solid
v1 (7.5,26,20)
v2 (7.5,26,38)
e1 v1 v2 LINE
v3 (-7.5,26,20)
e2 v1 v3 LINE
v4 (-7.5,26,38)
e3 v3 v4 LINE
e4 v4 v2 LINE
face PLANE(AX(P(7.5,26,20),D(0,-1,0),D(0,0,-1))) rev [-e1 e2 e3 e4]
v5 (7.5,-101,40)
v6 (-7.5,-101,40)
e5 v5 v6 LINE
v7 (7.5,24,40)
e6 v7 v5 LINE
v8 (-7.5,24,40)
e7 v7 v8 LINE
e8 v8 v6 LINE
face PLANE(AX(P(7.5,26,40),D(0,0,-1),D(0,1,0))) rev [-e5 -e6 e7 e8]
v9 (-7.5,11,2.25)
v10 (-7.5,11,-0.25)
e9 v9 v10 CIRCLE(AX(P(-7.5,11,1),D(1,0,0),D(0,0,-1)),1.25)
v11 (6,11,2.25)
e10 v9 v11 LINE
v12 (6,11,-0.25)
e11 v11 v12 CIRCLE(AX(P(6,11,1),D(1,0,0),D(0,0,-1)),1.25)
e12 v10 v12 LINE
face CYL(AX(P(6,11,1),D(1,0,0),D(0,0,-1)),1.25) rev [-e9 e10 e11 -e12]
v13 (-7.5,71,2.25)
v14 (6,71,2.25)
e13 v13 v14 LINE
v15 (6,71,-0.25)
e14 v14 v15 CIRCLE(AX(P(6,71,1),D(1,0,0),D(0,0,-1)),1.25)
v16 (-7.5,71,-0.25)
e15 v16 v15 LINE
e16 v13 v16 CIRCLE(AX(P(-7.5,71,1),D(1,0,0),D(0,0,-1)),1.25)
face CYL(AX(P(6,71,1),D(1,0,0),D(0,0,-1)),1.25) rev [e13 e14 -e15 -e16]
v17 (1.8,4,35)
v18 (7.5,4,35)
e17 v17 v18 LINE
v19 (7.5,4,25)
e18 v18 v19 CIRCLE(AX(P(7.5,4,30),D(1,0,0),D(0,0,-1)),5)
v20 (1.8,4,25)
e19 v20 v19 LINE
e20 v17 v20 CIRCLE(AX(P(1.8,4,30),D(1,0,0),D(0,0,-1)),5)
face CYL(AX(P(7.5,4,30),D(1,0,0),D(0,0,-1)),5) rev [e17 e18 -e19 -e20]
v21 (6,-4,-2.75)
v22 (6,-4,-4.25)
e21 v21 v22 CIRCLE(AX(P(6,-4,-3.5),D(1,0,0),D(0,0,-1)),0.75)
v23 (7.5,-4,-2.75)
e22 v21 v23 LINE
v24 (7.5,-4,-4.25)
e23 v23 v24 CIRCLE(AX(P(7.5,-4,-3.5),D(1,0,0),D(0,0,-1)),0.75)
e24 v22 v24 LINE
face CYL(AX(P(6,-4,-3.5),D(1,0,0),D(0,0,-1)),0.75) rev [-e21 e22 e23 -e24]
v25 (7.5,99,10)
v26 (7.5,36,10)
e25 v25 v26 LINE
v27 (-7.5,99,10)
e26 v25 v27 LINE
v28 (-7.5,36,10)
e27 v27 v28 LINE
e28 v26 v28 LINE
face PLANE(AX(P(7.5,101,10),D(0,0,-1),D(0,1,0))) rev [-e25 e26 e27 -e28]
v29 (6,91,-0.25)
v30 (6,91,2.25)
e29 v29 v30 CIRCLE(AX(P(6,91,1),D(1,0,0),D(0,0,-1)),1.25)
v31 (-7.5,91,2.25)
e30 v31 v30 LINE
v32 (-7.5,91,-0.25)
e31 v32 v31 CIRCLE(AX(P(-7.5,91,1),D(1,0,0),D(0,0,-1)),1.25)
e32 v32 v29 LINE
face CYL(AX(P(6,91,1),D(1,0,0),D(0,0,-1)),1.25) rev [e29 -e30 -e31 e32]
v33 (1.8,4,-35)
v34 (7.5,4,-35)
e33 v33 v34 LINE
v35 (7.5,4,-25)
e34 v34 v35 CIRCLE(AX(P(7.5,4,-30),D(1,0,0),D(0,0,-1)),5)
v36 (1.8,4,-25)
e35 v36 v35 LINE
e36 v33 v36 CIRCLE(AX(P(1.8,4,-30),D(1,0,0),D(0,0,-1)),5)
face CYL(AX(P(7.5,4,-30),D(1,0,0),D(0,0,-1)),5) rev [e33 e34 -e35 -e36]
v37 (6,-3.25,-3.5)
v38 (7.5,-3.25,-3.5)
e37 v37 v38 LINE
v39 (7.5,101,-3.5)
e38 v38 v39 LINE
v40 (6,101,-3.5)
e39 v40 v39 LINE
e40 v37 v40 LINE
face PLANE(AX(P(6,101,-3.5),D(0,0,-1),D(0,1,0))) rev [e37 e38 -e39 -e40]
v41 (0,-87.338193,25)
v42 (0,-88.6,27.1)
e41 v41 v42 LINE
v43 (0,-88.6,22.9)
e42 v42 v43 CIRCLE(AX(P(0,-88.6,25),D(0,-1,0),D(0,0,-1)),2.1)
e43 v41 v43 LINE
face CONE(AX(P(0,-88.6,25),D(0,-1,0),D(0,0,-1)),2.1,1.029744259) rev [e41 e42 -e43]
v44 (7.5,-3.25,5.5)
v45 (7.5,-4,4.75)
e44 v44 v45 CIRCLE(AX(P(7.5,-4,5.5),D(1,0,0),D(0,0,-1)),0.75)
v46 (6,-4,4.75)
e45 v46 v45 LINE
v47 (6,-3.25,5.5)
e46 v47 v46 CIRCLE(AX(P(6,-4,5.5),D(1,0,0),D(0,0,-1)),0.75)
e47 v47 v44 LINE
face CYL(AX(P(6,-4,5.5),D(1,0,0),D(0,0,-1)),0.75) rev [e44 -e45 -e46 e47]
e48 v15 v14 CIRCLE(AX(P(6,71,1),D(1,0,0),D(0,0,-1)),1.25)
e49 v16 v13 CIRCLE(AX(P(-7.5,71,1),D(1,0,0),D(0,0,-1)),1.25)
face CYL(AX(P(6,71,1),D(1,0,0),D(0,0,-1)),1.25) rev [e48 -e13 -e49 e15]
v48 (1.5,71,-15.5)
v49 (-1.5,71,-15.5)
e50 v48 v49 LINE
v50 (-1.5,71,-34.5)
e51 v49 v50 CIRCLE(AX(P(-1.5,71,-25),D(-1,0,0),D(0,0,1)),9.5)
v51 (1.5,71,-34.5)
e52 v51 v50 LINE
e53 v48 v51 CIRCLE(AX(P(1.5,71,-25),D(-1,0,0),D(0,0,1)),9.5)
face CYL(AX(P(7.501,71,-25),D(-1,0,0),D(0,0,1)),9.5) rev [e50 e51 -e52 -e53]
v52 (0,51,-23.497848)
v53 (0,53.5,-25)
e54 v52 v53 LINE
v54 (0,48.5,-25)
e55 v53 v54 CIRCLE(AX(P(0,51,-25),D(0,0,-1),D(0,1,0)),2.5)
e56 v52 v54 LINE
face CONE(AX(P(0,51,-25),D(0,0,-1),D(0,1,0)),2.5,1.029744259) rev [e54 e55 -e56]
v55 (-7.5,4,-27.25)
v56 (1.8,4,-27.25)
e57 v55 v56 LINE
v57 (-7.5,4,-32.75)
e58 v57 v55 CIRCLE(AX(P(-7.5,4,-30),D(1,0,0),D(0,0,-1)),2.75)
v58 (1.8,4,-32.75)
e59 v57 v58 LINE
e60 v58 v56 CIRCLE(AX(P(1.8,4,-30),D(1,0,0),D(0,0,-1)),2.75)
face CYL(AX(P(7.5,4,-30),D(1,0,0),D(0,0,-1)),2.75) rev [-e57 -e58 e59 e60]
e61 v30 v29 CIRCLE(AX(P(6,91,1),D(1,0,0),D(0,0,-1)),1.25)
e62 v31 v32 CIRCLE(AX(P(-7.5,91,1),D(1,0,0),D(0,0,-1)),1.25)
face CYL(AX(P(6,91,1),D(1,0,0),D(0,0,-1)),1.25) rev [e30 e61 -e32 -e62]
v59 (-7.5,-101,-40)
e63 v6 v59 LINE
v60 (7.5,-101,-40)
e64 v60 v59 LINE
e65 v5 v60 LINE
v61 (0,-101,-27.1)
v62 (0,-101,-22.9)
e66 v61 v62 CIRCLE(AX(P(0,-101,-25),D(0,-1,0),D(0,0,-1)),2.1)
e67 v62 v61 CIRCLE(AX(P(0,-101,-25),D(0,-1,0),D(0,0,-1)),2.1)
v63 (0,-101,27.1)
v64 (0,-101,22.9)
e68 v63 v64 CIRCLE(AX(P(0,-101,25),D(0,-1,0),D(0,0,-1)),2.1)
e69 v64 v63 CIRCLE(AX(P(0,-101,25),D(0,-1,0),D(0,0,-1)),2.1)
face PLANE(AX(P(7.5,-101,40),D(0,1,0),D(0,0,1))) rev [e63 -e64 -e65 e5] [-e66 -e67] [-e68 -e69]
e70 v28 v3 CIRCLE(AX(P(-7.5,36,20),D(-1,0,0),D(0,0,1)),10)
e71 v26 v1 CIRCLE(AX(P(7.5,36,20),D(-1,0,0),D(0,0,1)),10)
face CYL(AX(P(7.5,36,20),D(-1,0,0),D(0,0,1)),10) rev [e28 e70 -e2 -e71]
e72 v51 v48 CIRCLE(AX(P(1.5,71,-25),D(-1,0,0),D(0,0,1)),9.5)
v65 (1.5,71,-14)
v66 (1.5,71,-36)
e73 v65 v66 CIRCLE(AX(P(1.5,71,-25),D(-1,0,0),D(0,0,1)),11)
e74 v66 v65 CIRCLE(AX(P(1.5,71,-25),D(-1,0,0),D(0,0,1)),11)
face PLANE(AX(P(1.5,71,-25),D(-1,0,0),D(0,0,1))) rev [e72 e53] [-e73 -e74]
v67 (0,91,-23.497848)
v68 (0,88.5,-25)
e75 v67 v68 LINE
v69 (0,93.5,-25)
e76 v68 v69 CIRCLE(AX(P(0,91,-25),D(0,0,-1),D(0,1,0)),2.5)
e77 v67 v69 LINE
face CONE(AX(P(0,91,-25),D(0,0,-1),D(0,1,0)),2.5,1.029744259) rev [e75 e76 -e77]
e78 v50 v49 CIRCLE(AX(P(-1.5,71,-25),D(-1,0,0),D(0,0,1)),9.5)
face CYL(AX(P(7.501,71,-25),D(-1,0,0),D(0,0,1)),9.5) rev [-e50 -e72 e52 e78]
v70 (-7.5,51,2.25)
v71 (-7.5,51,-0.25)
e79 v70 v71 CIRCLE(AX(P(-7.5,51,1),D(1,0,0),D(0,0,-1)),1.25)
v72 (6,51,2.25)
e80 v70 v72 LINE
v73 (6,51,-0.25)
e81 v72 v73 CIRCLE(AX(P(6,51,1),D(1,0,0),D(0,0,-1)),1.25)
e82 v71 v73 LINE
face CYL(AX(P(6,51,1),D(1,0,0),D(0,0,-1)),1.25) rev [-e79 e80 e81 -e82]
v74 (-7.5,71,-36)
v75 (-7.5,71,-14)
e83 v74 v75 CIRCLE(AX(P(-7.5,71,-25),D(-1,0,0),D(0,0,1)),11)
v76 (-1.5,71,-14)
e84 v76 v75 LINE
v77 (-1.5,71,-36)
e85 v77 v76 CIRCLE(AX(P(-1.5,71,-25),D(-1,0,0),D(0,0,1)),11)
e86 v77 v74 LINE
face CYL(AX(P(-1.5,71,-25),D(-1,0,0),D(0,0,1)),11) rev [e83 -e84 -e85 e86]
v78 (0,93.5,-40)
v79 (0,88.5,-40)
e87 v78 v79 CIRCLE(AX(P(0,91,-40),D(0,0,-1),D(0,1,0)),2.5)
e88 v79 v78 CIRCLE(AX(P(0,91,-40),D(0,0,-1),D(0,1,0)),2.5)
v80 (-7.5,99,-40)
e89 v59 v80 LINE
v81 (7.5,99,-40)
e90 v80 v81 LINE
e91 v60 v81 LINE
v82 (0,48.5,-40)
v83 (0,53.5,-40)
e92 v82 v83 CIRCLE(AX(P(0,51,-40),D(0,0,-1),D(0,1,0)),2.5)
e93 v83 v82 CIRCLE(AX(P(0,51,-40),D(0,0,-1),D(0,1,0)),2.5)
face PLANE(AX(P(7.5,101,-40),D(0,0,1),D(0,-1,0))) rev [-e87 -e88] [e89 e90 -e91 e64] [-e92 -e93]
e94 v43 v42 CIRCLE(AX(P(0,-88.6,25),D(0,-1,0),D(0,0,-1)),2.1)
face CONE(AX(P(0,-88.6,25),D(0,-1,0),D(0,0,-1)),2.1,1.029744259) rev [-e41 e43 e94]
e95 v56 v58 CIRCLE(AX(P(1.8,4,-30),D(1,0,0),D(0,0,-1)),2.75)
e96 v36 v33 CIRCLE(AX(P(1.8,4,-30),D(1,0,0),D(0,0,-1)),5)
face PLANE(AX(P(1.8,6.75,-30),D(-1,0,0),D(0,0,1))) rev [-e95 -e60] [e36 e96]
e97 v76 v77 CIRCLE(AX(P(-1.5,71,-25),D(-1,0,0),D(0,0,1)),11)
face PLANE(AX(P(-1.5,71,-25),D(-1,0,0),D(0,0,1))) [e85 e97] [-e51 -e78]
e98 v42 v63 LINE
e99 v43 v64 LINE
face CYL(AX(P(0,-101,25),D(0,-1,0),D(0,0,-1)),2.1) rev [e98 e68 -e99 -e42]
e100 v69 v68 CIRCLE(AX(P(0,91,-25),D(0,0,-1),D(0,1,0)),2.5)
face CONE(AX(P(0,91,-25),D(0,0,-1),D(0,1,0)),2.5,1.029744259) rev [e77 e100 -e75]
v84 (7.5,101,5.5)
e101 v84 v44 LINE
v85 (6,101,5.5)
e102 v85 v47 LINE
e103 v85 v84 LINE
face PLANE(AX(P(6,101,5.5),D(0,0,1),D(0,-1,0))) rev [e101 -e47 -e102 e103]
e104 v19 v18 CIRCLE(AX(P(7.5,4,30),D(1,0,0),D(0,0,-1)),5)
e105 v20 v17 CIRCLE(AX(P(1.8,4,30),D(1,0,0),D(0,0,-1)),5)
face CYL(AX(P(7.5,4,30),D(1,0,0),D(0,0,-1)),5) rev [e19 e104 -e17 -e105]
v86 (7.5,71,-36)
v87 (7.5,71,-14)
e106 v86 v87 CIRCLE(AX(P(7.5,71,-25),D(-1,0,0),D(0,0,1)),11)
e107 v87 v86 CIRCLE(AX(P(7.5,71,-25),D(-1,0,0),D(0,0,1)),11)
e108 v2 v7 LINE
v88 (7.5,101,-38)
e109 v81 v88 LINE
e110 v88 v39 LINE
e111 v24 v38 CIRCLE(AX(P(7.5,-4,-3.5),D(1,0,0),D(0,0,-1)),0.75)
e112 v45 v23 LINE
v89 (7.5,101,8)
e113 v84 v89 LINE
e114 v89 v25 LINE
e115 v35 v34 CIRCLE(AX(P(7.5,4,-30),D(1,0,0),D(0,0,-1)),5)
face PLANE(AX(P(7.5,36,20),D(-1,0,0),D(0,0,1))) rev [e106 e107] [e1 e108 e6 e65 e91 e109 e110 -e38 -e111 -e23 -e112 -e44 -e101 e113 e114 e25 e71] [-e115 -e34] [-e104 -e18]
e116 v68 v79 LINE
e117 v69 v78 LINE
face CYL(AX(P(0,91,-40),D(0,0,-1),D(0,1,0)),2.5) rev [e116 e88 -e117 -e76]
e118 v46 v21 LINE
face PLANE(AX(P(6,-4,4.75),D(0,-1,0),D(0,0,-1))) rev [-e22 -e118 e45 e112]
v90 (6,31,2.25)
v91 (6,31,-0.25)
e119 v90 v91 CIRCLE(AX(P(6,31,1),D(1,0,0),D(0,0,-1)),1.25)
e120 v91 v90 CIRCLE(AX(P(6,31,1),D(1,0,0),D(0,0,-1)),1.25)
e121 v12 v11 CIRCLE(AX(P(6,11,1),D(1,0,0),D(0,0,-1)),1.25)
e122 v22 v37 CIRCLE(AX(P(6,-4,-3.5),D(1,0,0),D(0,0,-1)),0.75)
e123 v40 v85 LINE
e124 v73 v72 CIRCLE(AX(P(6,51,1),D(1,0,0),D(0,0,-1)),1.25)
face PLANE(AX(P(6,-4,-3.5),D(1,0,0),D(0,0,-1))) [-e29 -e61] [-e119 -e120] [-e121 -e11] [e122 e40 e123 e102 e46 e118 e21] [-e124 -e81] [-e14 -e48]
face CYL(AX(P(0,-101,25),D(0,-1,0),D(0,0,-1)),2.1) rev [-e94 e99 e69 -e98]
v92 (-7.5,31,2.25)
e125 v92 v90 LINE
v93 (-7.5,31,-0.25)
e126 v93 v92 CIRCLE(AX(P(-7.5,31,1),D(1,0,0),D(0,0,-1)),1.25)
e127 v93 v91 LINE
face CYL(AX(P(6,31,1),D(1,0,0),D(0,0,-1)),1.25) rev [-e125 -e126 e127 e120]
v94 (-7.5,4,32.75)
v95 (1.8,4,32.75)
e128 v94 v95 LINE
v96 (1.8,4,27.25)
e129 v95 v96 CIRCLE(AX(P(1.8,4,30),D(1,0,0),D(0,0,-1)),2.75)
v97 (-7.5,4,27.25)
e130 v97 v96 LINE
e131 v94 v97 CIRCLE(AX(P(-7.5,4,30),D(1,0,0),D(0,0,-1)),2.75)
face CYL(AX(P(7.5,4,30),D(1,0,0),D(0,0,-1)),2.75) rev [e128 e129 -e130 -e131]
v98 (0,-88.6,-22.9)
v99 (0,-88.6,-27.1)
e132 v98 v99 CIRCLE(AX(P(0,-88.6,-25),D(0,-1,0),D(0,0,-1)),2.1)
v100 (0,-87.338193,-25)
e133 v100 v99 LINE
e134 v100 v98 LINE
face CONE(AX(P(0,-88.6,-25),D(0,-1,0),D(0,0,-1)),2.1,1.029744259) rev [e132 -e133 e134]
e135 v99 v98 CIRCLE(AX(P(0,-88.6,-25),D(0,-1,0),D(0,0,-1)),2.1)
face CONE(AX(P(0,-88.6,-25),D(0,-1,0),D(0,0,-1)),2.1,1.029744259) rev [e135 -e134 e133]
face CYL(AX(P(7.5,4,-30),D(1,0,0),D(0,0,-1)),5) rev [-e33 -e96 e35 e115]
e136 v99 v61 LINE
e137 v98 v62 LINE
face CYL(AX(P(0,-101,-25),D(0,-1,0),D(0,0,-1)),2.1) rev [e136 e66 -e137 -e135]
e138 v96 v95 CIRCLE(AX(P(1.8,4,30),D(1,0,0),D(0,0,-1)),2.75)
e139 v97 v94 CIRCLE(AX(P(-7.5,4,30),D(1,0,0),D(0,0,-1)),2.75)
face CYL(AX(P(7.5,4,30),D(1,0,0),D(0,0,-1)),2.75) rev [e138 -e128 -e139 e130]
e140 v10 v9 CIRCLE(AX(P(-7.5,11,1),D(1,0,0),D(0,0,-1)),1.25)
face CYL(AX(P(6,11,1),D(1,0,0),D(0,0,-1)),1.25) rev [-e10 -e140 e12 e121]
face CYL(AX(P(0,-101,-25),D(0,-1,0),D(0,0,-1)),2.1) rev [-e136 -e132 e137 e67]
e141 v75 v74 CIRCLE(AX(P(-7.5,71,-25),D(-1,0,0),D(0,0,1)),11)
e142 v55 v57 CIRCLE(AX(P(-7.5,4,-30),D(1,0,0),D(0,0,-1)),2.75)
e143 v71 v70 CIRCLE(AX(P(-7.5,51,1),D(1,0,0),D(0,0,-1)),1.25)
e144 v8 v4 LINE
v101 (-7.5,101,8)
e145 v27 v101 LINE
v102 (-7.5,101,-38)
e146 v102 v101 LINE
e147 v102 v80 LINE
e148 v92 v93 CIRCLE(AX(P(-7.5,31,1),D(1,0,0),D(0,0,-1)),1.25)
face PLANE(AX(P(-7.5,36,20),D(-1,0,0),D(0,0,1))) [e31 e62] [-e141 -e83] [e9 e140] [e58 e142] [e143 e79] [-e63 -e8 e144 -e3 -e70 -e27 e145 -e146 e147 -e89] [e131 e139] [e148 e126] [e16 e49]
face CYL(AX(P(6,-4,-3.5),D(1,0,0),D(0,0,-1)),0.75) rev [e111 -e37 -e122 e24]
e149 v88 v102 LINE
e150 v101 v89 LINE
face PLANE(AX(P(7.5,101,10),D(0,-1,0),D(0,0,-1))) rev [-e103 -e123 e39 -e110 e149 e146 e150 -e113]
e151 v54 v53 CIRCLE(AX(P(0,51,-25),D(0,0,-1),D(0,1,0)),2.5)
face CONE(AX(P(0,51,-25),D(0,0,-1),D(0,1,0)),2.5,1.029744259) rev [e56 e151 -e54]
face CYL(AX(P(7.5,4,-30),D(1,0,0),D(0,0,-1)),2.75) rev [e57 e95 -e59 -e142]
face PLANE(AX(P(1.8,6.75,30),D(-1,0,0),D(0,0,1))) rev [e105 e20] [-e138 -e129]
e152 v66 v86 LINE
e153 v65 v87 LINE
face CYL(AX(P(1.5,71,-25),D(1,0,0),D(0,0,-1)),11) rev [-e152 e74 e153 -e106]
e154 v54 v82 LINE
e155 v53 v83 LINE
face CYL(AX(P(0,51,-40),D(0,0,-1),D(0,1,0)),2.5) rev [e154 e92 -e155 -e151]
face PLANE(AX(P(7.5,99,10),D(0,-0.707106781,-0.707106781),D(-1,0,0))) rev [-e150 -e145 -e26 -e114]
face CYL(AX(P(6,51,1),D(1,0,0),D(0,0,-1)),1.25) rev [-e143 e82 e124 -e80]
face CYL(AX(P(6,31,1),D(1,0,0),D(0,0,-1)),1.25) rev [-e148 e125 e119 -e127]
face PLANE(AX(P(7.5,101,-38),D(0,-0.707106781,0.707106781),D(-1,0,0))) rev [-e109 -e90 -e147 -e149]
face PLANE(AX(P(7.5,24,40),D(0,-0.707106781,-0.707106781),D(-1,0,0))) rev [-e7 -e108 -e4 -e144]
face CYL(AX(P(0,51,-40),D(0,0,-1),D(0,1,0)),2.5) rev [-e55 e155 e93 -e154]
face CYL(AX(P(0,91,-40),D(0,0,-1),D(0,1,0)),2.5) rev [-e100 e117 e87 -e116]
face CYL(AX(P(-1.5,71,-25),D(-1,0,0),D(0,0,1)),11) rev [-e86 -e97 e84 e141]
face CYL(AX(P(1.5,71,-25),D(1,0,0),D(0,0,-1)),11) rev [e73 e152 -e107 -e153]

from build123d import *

# Parameters (mm, degrees)
EXTRUDE_1_DEPTH           = 7.5
SKETCH_2_R                = 11
CUT_EXTRUDE_1_DEPTH       = 6
CUT_EXTRUDE_2_REACH       = 111.663
SKETCH_3_R                = 9.5
CUT_EXTRUDE_3_DEPTH       = 1.5
HOLE_WIZARD_M5_1_D        = 4.2
HOLE_WIZARD_M5_1_DEPTH    = 12.4
HOLE_WIZARD_M5_1_TIP      = 1.2618073
HOLE_WIZARD_1_D           = 5.5
HOLE_WIZARD_1_CBORE_D     = 10
HOLE_WIZARD_1_CBORE_DEPTH = 5.7
HOLE_WIZARD_M3_2_D        = 2.5
CUT_EXTRUDE_START         = -6
SKETCH_17_R               = 11
CUT_EXTRUDE_4_DEPTH       = 6
HOLE_WIZARD_M6_1_D        = 5
HOLE_WIZARD_M6_1_DEPTH    = 15
HOLE_WIZARD_M6_1_TIP      = 1.502151548
CHAMFER_1_SIZE            = 2


with BuildPart() as part:
    # 草图1 → 凸台-拉伸1 (new, symmetric)
    with BuildSketch(Plane(origin=(0, 0, 0), x_dir=(0, 0, -1), z_dir=(1, 0, 0))):
        with BuildLine():
            Line((-10, 101), (-10, 36))
            ThreePointArc((-10, 36), (-12.928932188, 28.928932188), (-20, 26))
            Line((-20, 26), (-40, 26))
            Line((-40, 26), (-40, -101))
            Line((-40, -101), (40, -101))
            Line((40, -101), (40, 101))
            Line((40, 101), (-10, 101))
        make_face()
    extrude(amount=EXTRUDE_1_DEPTH, both=True)

    # 草图2 → 切除-拉伸1 (cut)
    with BuildSketch(Plane.ZY.offset(-7.5)):
        with Locations((-25, 71)):
            Circle(SKETCH_2_R)
    extrude(amount=CUT_EXTRUDE_1_DEPTH, mode=Mode.SUBTRACT)

    # 草图3 → 切除-拉伸2 (cut, up to next)
    with BuildSketch(Plane(origin=(-7.5, 0, 0), x_dir=(0, 0, -1), z_dir=(1, 0, 0)), mode=Mode.PRIVATE) as cut_extrude_2_sk1:
        with Locations(Location((25, 71, 0), (0, 0, 180))):
            Circle(SKETCH_3_R)
    cut_extrude_2_tool1 = extrude(cut_extrude_2_sk1.sketch, amount=CUT_EXTRUDE_2_REACH, mode=Mode.PRIVATE) & part.part
    add(cut_extrude_2_tool1.solids().sort_by_distance((-7.5, 71, -25))[0], mode=Mode.SUBTRACT)

    # 草图6 → 切除-拉伸3 (cut)
    with BuildSketch(Plane(origin=(7.5, 0, 0), x_dir=(0, 0, -1), z_dir=(1, 0, 0))):
        with BuildLine():
            Line((-5.5, 101), (3.5, 101))
            Line((3.5, 101), (3.5, -3.25))
            ThreePointArc((3.5, -3.25), (4.030330086, -4.530330086), (2.75, -4))
            Line((2.75, -4), (-4.75, -4))
            ThreePointArc((-4.75, -4), (-6.030330086, -4.530330086), (-5.5, -3.25))
            Line((-5.5, -3.25), (-5.5, 101))
        make_face()
    extrude(amount=-CUT_EXTRUDE_3_DEPTH, mode=Mode.SUBTRACT)

    # M5 螺纹孔1
    with Locations(Plane(origin=(0, -101, 0), x_dir=(-1, 0, 0), z_dir=(0, -1, 0))):
        with Locations((0, 25), (0, -25)):
            Hole(HOLE_WIZARD_M5_1_D / 2, depth=HOLE_WIZARD_M5_1_DEPTH)
            with Locations((0, 0, -(HOLE_WIZARD_M5_1_DEPTH + HOLE_WIZARD_M5_1_TIP / 2))):  # 118° drill point
                Cone(0, HOLE_WIZARD_M5_1_D / 2, HOLE_WIZARD_M5_1_TIP, mode=Mode.SUBTRACT)

    # 打孔尺寸(%根据)内六角圆柱头螺钉的类型1 (through all)
    with Locations(Plane(origin=(7.5, 0, 0), x_dir=(0, 0, -1), z_dir=(1, 0, 0))):
        with Locations((30, 4), (-30, 4)):
            CounterBoreHole(HOLE_WIZARD_1_D / 2, HOLE_WIZARD_1_CBORE_D / 2, HOLE_WIZARD_1_CBORE_DEPTH)

    # M3 螺纹孔2 (through all)
    with Locations(Plane(origin=(6, 0, 0), x_dir=(0, 0, -1), z_dir=(1, 0, 0))):
        with Locations((-1, 91), (-1, 71), (-1, 51), (-1, 31), (-1, 11)):
            Hole(HOLE_WIZARD_M3_2_D / 2)

    # 草图17 → 切除-拉伸4 (cut)
    with BuildSketch(Plane.ZY.offset(7.5).offset(CUT_EXTRUDE_START)):
        with Locations((-25, 71)):
            Circle(SKETCH_17_R)
    extrude(amount=CUT_EXTRUDE_4_DEPTH, mode=Mode.SUBTRACT)

    # M6 螺纹孔1
    with Locations(Plane(origin=(0, 0, -40), x_dir=(-1, 0, 0), z_dir=(0, 0, -1))):
        with Locations((0, 51), (0, 91)):
            Hole(HOLE_WIZARD_M6_1_D / 2, depth=HOLE_WIZARD_M6_1_DEPTH)
            with Locations((0, 0, -(HOLE_WIZARD_M6_1_DEPTH + HOLE_WIZARD_M6_1_TIP / 2))):  # 118° drill point
                Cone(0, HOLE_WIZARD_M6_1_D / 2, HOLE_WIZARD_M6_1_TIP, mode=Mode.SUBTRACT)

    # 倒角1
    chamfer_1_edges = [part.edges().sort_by_distance(p)[0] for p in [
        (0, 26, 40),
        (0, 101, 10),
        (0, 101, -40),
    ]]
    chamfer(chamfer_1_edges, length=CHAMFER_1_SIZE)


solid = part.part
